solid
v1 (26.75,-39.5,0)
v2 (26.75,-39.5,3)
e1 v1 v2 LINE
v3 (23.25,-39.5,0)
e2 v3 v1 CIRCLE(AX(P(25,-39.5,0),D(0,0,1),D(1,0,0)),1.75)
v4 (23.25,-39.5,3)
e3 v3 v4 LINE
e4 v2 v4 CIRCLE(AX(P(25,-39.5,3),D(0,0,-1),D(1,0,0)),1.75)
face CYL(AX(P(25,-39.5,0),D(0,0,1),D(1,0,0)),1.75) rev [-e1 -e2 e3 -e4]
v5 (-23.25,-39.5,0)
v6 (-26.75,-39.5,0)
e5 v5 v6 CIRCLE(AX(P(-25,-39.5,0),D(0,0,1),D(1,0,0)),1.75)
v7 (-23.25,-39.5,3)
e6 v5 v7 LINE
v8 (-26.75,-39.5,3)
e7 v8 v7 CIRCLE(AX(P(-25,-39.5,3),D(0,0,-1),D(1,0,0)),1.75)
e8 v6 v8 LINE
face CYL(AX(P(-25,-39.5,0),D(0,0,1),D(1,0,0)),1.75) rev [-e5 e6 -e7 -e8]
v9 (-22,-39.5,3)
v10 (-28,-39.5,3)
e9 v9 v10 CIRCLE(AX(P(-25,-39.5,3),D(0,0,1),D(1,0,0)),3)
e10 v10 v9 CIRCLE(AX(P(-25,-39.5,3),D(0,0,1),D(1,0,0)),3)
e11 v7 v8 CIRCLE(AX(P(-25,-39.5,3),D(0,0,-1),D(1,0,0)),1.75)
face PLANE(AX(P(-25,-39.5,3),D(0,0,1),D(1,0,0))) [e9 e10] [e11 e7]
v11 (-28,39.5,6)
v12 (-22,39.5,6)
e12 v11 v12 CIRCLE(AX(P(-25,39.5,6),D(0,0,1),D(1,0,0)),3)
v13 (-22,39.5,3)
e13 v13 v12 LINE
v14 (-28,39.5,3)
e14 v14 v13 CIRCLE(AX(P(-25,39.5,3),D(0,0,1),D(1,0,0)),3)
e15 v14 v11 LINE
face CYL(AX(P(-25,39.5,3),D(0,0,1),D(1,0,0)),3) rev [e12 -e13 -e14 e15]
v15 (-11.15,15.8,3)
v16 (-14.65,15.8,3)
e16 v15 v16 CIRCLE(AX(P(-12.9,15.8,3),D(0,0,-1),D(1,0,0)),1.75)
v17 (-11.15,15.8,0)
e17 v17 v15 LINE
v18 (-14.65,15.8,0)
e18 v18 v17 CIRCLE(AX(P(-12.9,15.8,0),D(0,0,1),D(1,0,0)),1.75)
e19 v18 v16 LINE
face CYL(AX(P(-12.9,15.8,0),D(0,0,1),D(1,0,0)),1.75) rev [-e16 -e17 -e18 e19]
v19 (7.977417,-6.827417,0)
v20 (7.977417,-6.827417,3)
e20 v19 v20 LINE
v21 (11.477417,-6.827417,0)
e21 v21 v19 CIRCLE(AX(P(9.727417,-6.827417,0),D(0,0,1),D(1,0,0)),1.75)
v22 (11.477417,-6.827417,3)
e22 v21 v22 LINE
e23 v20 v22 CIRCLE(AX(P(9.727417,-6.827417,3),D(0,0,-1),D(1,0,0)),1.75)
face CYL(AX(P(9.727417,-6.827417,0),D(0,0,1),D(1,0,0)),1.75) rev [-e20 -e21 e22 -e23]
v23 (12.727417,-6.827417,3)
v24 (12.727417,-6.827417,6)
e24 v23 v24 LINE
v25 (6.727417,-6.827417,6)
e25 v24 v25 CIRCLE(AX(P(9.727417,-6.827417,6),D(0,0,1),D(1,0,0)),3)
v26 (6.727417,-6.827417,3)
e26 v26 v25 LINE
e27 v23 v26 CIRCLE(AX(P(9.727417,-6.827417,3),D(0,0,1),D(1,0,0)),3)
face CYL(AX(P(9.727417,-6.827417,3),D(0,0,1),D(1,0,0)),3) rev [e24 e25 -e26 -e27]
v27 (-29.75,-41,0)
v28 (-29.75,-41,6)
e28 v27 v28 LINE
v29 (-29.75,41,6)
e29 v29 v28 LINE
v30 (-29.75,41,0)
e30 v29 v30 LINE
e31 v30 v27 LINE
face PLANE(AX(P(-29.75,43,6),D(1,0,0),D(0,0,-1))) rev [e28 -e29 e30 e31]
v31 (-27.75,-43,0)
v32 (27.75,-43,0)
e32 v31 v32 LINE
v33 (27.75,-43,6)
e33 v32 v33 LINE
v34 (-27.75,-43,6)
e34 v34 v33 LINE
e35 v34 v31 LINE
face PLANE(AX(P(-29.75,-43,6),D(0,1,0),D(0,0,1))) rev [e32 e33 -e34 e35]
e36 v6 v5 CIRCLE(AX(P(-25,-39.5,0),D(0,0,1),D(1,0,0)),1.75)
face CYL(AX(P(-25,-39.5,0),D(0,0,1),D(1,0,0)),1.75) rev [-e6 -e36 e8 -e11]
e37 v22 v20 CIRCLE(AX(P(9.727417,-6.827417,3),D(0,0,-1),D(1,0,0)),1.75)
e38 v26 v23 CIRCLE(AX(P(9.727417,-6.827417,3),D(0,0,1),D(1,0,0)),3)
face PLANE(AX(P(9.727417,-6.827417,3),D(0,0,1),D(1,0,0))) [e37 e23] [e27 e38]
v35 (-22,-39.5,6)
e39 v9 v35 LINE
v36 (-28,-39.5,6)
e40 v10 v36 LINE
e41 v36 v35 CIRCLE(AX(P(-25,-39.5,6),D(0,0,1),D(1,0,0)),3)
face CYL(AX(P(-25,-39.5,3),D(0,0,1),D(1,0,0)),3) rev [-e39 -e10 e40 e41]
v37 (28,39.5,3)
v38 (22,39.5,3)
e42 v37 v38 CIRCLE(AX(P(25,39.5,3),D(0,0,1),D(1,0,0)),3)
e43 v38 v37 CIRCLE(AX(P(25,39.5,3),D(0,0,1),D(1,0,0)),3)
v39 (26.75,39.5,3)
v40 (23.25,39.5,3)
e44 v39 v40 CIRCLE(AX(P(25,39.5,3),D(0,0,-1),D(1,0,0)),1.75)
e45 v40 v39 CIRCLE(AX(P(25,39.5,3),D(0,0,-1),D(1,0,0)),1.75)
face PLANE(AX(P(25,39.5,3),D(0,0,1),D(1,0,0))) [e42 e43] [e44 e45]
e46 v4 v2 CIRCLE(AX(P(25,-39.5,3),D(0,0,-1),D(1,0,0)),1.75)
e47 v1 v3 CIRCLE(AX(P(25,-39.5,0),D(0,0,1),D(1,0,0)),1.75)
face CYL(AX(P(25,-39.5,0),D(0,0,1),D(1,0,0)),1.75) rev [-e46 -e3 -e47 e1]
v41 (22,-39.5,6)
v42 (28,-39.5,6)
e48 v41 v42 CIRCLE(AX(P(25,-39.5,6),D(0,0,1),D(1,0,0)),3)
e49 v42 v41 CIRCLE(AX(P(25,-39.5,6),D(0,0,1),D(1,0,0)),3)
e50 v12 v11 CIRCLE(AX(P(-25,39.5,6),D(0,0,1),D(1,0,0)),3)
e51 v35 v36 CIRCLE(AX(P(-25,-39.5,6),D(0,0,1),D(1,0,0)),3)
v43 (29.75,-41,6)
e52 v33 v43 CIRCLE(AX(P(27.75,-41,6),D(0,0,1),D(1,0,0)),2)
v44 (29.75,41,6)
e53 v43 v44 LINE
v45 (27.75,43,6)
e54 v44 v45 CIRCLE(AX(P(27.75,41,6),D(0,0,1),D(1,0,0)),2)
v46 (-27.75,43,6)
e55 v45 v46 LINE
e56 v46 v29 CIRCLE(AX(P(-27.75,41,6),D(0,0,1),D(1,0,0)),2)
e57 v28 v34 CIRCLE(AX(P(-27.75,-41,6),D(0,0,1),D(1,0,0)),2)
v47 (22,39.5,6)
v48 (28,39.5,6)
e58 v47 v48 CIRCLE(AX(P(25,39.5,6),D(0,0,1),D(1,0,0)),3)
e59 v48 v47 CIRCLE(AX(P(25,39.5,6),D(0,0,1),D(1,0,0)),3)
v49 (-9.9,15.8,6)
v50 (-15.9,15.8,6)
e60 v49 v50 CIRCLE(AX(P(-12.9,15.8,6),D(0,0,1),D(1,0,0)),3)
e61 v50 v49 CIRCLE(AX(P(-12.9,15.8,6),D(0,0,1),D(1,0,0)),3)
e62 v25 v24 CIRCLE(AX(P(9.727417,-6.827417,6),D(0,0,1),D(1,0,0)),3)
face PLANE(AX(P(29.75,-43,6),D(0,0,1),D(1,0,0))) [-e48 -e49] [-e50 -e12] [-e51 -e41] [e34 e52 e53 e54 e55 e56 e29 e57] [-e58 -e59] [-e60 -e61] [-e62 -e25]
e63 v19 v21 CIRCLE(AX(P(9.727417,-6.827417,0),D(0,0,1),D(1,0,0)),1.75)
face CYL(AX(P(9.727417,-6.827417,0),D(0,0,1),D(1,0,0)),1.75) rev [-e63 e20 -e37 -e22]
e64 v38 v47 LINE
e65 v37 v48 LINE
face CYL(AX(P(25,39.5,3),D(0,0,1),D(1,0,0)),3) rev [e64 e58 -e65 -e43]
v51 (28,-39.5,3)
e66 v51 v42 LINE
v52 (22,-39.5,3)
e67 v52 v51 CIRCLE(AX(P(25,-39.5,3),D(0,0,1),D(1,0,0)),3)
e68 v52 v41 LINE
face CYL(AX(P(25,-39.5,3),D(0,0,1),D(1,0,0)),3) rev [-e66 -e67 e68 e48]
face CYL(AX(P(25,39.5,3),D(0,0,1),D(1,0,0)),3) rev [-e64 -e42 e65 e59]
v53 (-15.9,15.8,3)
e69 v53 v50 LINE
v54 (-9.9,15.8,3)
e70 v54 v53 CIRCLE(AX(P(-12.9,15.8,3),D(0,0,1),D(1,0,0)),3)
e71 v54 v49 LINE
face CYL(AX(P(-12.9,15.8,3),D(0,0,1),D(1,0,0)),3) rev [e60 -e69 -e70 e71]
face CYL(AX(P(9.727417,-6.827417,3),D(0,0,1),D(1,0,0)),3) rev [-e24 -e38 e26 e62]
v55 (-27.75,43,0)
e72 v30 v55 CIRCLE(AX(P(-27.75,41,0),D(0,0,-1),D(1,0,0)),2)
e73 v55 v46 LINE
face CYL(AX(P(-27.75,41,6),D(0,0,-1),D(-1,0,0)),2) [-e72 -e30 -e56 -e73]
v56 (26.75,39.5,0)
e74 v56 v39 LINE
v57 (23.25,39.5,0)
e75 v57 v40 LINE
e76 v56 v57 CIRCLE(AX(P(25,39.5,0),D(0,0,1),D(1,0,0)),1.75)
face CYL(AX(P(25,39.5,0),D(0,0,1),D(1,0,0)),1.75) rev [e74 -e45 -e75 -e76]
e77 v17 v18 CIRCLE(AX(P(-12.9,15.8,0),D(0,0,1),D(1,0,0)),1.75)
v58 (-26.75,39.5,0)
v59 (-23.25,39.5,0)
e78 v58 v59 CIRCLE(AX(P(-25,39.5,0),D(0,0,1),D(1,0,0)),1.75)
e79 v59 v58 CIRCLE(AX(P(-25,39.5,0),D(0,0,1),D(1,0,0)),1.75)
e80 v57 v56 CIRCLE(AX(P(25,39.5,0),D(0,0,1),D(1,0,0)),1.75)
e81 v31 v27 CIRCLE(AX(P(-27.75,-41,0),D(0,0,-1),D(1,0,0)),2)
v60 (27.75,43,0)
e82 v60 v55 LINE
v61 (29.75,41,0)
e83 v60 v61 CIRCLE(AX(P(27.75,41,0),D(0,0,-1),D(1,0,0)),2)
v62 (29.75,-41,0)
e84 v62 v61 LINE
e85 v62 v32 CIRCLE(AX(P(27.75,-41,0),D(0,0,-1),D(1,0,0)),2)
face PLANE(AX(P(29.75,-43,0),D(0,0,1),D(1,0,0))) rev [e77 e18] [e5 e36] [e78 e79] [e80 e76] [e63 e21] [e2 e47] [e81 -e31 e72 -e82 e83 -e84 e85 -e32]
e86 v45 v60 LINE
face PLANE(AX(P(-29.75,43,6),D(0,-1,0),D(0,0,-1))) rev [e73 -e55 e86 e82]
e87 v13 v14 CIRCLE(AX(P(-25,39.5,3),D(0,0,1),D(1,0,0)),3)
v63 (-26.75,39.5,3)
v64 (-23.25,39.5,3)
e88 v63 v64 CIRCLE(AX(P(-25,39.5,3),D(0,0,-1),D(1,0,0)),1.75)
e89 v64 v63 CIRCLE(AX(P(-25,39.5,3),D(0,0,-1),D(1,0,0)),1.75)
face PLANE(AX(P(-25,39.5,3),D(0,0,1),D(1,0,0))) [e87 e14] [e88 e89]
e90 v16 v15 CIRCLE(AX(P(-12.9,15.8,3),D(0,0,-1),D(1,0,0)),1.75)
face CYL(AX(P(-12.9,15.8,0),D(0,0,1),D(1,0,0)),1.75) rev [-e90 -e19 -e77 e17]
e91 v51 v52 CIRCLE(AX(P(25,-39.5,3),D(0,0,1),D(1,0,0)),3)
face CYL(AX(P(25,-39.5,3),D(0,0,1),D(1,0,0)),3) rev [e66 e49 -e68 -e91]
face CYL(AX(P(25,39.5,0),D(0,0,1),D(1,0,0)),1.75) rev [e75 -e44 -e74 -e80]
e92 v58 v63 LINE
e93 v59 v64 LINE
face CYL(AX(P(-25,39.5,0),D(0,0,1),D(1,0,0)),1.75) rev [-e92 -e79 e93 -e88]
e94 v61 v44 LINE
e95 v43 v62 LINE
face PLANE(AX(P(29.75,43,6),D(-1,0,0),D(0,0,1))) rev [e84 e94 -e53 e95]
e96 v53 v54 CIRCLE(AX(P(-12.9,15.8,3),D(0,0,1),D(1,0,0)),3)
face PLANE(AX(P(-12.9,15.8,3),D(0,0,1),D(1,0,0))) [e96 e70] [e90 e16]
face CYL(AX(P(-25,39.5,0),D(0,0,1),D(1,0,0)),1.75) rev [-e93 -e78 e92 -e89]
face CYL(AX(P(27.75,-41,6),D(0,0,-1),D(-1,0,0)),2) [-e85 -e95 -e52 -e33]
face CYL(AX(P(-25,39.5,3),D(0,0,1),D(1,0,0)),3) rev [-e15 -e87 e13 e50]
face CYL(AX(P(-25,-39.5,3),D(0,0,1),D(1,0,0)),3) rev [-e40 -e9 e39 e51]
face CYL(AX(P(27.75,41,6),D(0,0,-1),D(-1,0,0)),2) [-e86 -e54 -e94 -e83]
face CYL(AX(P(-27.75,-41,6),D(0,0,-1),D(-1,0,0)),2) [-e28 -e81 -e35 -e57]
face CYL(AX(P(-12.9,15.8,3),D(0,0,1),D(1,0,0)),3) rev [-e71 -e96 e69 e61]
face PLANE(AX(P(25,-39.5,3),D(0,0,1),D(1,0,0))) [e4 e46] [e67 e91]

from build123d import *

# Parameters (mm, degrees)
SKETCH_1_W          = 59.5
SKETCH_1_H          = 86
EXTRUDE_1_DEPTH     = 6
SKETCH_2_R          = 1.75
CUT_EXTRUDE_1_DEPTH = 6
SKETCH_3_R          = 3
CUT_EXTRUDE_2_DEPTH = 3
FILLET_1_R          = 2


with BuildPart() as part:
    # 草图1 → 凸台-拉伸1 (new body)
    with BuildSketch(Plane.XY):
        Rectangle(SKETCH_1_W, SKETCH_1_H)
    extrude(amount=EXTRUDE_1_DEPTH)

    # 草图2 → 切除-拉伸1 (cut)
    with BuildSketch(Plane.XY.offset(6)):
        with Locations((-25, -39.5)):
            Circle(SKETCH_2_R)
        with Locations((25, -39.5)):
            Circle(SKETCH_2_R)
        with Locations((25, 39.5)):
            Circle(SKETCH_2_R)
        with Locations((-25, 39.5)):
            Circle(SKETCH_2_R)
        with Locations((-12.9, 15.8)):
            Circle(SKETCH_2_R)
        with Locations((9.727416998, -6.827416998)):
            Circle(SKETCH_2_R)
    extrude(amount=-CUT_EXTRUDE_1_DEPTH, mode=Mode.SUBTRACT)

    # 草图3 → 切除-拉伸2 (cut)
    with BuildSketch(Plane.XY.offset(6)):
        with Locations((-25, 39.5)):
            Circle(SKETCH_3_R)
        with Locations((25, 39.5)):
            Circle(SKETCH_3_R)
        with Locations((-12.9, 15.8)):
            Circle(SKETCH_3_R)
        with Locations((9.727416998, -6.827416998)):
            Circle(SKETCH_3_R)
        with Locations((-25, -39.5)):
            Circle(SKETCH_3_R)
        with Locations((25, -39.5)):
            Circle(SKETCH_3_R)
    extrude(amount=-CUT_EXTRUDE_2_DEPTH, mode=Mode.SUBTRACT)

    # 圆角1
    fillet_1_edges = [part.edges().sort_by_distance(p)[0] for p in [
        (29.75, -43, 3),
        (-29.75, -43, 3),
        (-29.75, 43, 3),
        (29.75, 43, 3),
    ]]
    fillet(fillet_1_edges, radius=FILLET_1_R)


solid = part.part
